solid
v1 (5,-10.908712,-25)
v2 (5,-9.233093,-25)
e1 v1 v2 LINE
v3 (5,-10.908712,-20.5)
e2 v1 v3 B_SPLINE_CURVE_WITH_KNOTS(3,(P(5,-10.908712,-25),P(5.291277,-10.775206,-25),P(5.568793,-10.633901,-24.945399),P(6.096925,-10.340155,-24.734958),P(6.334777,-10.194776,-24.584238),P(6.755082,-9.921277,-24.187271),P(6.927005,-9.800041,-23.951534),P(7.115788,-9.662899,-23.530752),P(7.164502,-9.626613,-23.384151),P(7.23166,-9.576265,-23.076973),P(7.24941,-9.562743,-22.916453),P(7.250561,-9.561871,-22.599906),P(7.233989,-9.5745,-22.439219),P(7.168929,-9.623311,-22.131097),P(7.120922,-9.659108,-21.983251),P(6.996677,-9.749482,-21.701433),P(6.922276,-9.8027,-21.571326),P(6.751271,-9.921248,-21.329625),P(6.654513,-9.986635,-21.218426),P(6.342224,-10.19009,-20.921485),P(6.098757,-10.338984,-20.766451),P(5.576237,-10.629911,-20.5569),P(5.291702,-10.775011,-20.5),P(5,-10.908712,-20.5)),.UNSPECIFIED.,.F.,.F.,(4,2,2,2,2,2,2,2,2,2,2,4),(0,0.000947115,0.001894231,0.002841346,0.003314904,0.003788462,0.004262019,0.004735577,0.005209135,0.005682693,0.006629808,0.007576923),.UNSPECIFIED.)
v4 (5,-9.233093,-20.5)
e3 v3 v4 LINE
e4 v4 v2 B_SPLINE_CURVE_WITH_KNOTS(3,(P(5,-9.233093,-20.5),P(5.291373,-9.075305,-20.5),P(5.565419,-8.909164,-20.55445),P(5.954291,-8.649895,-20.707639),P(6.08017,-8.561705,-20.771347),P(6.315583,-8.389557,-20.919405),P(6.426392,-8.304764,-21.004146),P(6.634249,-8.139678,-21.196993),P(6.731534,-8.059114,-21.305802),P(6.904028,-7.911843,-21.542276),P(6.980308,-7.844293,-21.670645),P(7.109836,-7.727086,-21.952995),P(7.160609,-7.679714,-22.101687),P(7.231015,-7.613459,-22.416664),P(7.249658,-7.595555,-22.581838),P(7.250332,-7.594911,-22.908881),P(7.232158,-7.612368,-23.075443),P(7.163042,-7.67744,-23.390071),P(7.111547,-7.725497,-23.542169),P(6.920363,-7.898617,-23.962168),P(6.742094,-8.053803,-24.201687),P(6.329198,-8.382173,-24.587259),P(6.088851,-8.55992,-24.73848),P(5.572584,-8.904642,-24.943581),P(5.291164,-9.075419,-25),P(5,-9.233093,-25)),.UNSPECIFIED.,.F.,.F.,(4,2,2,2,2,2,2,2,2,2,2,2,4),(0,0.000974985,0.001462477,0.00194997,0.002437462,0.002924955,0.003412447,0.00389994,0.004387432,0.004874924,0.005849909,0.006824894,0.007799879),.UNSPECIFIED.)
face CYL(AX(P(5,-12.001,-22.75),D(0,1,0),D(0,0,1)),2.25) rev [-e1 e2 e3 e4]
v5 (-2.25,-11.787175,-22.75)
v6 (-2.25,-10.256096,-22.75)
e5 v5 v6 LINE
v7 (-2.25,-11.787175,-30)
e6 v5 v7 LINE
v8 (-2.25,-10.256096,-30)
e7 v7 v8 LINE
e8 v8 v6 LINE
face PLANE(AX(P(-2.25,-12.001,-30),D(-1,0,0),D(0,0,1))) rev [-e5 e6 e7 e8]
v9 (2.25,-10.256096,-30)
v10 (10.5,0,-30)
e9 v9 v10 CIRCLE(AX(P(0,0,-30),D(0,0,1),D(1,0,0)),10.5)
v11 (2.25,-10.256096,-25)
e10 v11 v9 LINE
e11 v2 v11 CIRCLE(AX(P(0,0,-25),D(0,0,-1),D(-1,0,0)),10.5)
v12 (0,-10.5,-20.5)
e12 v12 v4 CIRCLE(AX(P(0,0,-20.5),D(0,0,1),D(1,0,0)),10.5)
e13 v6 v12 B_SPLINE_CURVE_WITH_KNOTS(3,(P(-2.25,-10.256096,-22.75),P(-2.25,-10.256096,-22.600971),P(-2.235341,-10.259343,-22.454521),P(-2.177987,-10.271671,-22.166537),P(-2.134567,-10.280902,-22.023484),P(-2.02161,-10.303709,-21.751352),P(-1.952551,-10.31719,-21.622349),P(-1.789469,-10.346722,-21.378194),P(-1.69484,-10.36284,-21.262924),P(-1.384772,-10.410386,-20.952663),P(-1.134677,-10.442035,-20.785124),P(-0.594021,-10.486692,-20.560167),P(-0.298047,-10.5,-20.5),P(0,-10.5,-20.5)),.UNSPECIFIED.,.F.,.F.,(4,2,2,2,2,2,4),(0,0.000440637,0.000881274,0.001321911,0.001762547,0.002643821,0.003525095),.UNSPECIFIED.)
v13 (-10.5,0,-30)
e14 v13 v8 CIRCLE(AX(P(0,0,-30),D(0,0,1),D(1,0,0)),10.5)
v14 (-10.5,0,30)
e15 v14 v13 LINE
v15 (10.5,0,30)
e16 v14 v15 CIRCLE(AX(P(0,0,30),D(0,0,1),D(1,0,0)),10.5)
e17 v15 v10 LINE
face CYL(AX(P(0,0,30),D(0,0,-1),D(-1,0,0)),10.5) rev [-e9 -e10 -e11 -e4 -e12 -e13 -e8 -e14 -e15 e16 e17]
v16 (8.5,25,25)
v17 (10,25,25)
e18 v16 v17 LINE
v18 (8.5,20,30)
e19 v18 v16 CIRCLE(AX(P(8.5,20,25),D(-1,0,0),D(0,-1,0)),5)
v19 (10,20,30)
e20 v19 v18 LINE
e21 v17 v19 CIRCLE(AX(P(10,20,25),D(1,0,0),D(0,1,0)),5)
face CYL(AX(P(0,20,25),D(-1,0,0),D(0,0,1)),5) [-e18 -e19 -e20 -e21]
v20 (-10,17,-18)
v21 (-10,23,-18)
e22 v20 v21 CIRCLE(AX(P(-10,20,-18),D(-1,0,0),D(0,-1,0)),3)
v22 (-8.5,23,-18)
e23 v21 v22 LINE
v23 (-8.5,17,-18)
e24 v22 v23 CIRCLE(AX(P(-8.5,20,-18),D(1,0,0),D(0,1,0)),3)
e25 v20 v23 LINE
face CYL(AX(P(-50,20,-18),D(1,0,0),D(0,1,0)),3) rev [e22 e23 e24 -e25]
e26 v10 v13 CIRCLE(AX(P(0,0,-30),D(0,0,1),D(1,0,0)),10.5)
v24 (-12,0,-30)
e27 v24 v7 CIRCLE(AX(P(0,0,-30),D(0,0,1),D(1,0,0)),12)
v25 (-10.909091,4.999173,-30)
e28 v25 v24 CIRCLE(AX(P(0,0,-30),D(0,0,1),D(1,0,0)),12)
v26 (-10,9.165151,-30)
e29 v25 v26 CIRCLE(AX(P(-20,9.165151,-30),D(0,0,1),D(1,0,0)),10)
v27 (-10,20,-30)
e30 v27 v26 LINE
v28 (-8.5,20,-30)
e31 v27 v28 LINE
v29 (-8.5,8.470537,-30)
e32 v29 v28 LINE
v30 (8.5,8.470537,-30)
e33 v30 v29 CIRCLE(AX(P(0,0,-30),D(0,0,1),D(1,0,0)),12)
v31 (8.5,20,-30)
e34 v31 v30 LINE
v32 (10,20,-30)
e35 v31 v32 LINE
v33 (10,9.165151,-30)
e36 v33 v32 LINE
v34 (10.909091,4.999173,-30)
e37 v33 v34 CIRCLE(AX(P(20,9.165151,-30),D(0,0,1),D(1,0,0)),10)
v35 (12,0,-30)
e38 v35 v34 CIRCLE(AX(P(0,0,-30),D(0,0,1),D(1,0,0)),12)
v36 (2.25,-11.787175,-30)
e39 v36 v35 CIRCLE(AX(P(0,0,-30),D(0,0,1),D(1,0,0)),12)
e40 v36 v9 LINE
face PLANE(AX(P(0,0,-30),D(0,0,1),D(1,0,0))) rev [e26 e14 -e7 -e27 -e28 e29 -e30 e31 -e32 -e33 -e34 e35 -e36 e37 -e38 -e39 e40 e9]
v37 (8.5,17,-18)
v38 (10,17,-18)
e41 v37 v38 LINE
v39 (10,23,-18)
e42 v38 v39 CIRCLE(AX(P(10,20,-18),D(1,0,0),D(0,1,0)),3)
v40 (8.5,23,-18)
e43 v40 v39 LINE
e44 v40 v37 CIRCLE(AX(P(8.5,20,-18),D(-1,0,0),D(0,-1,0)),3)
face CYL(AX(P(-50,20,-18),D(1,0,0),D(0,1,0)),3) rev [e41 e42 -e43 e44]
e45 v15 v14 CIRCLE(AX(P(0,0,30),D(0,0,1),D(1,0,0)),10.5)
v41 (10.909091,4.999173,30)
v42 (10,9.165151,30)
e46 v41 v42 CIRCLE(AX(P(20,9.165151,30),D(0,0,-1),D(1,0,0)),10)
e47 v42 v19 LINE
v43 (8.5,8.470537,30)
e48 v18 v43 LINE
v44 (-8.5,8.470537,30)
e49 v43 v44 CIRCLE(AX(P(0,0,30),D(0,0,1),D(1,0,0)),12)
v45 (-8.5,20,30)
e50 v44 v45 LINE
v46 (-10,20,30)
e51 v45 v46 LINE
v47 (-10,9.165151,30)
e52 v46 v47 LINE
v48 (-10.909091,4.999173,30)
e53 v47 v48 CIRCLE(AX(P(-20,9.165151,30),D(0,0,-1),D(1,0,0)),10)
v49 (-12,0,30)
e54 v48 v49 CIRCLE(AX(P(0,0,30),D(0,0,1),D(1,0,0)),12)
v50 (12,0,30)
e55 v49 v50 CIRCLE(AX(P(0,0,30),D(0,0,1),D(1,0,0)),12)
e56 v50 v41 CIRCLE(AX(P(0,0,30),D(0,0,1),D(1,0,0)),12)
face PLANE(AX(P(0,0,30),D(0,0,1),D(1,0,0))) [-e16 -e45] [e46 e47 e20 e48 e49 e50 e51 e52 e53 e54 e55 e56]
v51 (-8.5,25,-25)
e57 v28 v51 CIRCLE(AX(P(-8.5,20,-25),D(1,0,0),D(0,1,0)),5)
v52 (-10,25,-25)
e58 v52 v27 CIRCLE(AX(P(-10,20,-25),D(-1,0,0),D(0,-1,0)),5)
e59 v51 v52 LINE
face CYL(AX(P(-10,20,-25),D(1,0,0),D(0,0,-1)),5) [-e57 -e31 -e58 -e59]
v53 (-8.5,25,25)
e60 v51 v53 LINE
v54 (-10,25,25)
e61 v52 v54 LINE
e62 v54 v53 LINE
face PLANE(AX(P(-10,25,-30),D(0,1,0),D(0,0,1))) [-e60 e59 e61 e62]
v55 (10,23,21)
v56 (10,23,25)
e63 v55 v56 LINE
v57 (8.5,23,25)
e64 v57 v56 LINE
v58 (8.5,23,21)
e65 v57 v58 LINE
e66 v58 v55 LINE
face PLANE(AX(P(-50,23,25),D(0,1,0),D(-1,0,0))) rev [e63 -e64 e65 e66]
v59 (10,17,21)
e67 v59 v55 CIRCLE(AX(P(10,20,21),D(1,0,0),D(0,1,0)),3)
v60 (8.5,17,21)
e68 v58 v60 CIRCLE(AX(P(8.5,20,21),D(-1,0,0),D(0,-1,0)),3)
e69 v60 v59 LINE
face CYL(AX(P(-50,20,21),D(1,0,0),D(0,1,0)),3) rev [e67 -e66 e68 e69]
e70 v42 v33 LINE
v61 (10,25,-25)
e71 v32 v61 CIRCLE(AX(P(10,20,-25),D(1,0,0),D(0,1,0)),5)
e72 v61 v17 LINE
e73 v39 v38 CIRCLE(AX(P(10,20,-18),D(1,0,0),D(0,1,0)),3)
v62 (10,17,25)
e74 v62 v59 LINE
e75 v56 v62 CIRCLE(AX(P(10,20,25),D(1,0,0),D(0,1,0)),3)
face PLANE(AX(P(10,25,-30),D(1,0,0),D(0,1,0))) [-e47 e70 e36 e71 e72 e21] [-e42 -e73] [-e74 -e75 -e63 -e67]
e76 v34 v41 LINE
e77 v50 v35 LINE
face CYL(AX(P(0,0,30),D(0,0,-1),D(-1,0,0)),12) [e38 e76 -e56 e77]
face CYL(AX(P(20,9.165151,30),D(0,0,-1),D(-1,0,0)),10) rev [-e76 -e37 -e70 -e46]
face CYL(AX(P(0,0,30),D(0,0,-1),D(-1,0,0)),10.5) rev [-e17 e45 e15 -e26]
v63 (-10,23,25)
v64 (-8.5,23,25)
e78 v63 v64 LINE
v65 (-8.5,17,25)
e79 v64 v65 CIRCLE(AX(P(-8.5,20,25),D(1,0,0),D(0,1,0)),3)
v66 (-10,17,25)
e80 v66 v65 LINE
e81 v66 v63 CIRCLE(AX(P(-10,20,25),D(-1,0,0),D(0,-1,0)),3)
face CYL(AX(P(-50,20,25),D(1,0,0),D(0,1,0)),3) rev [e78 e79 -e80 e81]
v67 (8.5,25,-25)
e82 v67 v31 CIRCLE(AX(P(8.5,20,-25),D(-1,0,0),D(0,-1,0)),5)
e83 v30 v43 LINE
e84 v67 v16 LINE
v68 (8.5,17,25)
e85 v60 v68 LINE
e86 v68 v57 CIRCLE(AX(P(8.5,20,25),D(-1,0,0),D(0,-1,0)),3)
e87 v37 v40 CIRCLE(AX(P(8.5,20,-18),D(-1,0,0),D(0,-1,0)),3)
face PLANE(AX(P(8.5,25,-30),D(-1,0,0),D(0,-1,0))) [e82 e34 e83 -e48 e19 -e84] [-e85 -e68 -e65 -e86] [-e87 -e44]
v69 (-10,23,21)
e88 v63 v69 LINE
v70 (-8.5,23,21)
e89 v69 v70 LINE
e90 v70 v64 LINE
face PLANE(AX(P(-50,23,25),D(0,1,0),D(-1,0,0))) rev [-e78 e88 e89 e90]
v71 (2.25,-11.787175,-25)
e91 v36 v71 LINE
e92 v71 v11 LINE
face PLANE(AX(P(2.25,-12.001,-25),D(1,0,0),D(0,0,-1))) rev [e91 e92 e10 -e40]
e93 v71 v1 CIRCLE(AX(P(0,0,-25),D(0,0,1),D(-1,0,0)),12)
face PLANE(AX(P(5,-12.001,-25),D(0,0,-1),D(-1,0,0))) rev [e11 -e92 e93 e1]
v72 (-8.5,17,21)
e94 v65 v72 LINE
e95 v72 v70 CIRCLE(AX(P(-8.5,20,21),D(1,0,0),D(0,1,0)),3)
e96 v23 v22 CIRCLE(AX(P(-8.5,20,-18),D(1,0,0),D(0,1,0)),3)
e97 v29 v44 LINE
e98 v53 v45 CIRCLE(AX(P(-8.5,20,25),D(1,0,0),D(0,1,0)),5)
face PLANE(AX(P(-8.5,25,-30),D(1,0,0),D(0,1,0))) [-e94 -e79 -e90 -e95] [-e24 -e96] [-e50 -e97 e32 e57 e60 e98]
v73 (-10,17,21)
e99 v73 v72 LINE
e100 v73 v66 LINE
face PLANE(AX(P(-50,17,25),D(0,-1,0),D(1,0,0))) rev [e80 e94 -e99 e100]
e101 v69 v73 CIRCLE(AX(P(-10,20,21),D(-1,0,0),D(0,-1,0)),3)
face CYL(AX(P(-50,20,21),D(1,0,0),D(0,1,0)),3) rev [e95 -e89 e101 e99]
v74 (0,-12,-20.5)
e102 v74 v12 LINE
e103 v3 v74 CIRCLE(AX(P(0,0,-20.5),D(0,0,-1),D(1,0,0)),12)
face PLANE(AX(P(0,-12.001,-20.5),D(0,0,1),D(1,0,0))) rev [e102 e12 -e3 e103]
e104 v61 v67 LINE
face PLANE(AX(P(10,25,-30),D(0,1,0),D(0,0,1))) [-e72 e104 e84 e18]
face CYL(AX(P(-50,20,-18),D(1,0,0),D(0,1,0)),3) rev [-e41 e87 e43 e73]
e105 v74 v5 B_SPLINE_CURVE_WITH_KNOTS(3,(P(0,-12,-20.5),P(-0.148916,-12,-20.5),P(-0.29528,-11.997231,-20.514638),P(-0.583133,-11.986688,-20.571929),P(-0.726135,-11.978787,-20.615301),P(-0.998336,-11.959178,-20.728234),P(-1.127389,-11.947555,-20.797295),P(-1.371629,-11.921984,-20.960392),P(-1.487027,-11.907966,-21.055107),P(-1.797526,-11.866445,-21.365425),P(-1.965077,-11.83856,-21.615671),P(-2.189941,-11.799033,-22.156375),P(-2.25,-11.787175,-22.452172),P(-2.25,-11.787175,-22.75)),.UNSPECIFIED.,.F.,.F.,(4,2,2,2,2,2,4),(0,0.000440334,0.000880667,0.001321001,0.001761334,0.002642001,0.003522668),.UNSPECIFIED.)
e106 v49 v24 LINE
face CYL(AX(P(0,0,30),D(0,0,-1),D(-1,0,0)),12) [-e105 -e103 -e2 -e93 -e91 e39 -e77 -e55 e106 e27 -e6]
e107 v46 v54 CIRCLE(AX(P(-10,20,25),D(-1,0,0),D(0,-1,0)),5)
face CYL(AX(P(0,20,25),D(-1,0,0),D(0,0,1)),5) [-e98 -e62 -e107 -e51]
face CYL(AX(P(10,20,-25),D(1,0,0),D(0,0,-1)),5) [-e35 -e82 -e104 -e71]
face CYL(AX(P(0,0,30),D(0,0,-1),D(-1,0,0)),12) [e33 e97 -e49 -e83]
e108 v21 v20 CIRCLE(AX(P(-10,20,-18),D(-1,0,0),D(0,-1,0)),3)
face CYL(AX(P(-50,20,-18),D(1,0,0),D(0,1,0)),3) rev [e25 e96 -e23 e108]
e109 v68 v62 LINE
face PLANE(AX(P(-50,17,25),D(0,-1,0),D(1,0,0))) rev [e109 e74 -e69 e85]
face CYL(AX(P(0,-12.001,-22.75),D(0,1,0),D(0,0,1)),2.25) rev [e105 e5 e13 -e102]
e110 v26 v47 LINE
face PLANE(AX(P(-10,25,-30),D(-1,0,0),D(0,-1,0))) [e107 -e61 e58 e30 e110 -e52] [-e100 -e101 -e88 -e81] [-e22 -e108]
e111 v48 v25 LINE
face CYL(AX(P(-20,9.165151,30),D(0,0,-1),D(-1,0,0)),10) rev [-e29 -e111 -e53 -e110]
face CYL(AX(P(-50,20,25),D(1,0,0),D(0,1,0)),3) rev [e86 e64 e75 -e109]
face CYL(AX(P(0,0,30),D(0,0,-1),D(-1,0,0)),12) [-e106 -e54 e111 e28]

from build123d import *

# Parameters (mm, degrees)
SLEEVE_TUBE_PROFILE_R   = 12
SLEEVE_TUBE_PROFILE_R_2 = 10.5
SLEEVE_TUBE_24X60_DEPTH = 30
MOUNTING_LUGS_DEPTH     = 60
LUG_FILLET_R10_R        = 10
LUG_FILLET_R5_R         = 5
LUG_GAP_CUT_PROFILE_R   = 3
LUG_GAP_CUT_DEPTH       = 60
LUG_SLOTS_REACH         = 42.853
LUG_SLOTS_END_RADIUS    = 12


with BuildPart() as part:
    # Sleeve Tube Profile → Sleeve Tube Ø24x60 (new, symmetric)
    with BuildSketch(Plane.XY):
        Circle(SLEEVE_TUBE_PROFILE_R)
        Circle(SLEEVE_TUBE_PROFILE_R_2, mode=Mode.SUBTRACT)
    extrude(amount=SLEEVE_TUBE_24X60_DEPTH, both=True)

    # Mounting Lugs Profile → Mounting Lugs (add)
    with BuildSketch(Plane.XY.offset(30)):
        with BuildLine():
            Line((-8.5, 25), (-8.5, 8.470537173))
            ThreePointArc((-8.5, 8.470537173), (-9.295504635, 7.589044312), (-10, 6.633249581))
            Line((-10, 6.633249581), (-10, 25))
            Line((-10, 25), (-8.5, 25))
        make_face()
        with BuildLine():
            Line((10, 25), (10, 6.633249581))
            ThreePointArc((10, 6.633249581), (9.295504635, 7.589044312), (8.5, 8.470537173))
            Line((8.5, 8.470537173), (8.5, 25))
            Line((8.5, 25), (10, 25))
        make_face()
    extrude(amount=-MOUNTING_LUGS_DEPTH)

    # Lug Fillet R10
    lug_fillet_r10_edges = [part.edges().sort_by_distance(p)[0] for p in [
        (-10, 6.633249581, 0),
        (10, 6.633249581, 0),
    ]]
    fillet(lug_fillet_r10_edges, radius=LUG_FILLET_R10_R)

    # Lug Fillet R5
    lug_fillet_r5_edges = [part.edges().sort_by_distance(p)[0] for p in [
        (-9.25, 25, -30),
        (-9.25, 25, 30),
        (9.25, 25, -30),
        (9.25, 25, 30),
    ]]
    fillet(lug_fillet_r5_edges, radius=LUG_FILLET_R5_R)

    # Lug Gap Cut Profile → Lug Gap Cut (cut)
    with BuildSketch(Plane(origin=(10, 0, 0), x_dir=(0, 0, -1), z_dir=(1, 0, 0))):
        with Locations(Location((18, 20, 0), (0, 0, 90))):
            Circle(LUG_GAP_CUT_PROFILE_R)
        with BuildLine():
            Line((-25, 23), (-21, 23))
            ThreePointArc((-21, 23), (-18, 20), (-21, 17))
            Line((-21, 17), (-25, 17))
            ThreePointArc((-25, 17), (-28, 20), (-25, 23))
        make_face()
    extrude(amount=-LUG_GAP_CUT_DEPTH, mode=Mode.SUBTRACT)

    # Lug Slots: up to this cylinder (the profile starts inside it)
    lug_slots_end = Plane(origin=(0, 0, -24.504673), z_dir=(0, 0, -1)) * Cylinder(LUG_SLOTS_END_RADIUS, 110.706, mode=Mode.PRIVATE)
    # Lug Slots Profile → Lug Slots (cut, up to the surface)
    with BuildSketch(Plane(origin=(0, 0, 0), x_dir=(1, 0, 0), z_dir=(0, 1, 0)), mode=Mode.PRIVATE) as lug_slots_sk1:
        with BuildLine():
            Line((-2.25, 30), (-2.25, 22.75))
            ThreePointArc((-2.25, 22.75), (-1.590990258, 21.159009742), (0, 20.5))
            Line((0, 20.5), (5, 20.5))
            ThreePointArc((5, 20.5), (7.25, 22.75), (5, 25))
            Line((5, 25), (2.25, 25))
            Line((2.25, 25), (2.25, 30))
            Line((2.25, 30), (-2.25, 30))
        make_face()
    lug_slots_tool1 = extrude(lug_slots_sk1.sketch, amount=-LUG_SLOTS_REACH, mode=Mode.PRIVATE) & lug_slots_end
    add(lug_slots_tool1.solids().sort_by_distance((1.518168, 0, -24.504673))[0], mode=Mode.SUBTRACT)


solid = part.part
